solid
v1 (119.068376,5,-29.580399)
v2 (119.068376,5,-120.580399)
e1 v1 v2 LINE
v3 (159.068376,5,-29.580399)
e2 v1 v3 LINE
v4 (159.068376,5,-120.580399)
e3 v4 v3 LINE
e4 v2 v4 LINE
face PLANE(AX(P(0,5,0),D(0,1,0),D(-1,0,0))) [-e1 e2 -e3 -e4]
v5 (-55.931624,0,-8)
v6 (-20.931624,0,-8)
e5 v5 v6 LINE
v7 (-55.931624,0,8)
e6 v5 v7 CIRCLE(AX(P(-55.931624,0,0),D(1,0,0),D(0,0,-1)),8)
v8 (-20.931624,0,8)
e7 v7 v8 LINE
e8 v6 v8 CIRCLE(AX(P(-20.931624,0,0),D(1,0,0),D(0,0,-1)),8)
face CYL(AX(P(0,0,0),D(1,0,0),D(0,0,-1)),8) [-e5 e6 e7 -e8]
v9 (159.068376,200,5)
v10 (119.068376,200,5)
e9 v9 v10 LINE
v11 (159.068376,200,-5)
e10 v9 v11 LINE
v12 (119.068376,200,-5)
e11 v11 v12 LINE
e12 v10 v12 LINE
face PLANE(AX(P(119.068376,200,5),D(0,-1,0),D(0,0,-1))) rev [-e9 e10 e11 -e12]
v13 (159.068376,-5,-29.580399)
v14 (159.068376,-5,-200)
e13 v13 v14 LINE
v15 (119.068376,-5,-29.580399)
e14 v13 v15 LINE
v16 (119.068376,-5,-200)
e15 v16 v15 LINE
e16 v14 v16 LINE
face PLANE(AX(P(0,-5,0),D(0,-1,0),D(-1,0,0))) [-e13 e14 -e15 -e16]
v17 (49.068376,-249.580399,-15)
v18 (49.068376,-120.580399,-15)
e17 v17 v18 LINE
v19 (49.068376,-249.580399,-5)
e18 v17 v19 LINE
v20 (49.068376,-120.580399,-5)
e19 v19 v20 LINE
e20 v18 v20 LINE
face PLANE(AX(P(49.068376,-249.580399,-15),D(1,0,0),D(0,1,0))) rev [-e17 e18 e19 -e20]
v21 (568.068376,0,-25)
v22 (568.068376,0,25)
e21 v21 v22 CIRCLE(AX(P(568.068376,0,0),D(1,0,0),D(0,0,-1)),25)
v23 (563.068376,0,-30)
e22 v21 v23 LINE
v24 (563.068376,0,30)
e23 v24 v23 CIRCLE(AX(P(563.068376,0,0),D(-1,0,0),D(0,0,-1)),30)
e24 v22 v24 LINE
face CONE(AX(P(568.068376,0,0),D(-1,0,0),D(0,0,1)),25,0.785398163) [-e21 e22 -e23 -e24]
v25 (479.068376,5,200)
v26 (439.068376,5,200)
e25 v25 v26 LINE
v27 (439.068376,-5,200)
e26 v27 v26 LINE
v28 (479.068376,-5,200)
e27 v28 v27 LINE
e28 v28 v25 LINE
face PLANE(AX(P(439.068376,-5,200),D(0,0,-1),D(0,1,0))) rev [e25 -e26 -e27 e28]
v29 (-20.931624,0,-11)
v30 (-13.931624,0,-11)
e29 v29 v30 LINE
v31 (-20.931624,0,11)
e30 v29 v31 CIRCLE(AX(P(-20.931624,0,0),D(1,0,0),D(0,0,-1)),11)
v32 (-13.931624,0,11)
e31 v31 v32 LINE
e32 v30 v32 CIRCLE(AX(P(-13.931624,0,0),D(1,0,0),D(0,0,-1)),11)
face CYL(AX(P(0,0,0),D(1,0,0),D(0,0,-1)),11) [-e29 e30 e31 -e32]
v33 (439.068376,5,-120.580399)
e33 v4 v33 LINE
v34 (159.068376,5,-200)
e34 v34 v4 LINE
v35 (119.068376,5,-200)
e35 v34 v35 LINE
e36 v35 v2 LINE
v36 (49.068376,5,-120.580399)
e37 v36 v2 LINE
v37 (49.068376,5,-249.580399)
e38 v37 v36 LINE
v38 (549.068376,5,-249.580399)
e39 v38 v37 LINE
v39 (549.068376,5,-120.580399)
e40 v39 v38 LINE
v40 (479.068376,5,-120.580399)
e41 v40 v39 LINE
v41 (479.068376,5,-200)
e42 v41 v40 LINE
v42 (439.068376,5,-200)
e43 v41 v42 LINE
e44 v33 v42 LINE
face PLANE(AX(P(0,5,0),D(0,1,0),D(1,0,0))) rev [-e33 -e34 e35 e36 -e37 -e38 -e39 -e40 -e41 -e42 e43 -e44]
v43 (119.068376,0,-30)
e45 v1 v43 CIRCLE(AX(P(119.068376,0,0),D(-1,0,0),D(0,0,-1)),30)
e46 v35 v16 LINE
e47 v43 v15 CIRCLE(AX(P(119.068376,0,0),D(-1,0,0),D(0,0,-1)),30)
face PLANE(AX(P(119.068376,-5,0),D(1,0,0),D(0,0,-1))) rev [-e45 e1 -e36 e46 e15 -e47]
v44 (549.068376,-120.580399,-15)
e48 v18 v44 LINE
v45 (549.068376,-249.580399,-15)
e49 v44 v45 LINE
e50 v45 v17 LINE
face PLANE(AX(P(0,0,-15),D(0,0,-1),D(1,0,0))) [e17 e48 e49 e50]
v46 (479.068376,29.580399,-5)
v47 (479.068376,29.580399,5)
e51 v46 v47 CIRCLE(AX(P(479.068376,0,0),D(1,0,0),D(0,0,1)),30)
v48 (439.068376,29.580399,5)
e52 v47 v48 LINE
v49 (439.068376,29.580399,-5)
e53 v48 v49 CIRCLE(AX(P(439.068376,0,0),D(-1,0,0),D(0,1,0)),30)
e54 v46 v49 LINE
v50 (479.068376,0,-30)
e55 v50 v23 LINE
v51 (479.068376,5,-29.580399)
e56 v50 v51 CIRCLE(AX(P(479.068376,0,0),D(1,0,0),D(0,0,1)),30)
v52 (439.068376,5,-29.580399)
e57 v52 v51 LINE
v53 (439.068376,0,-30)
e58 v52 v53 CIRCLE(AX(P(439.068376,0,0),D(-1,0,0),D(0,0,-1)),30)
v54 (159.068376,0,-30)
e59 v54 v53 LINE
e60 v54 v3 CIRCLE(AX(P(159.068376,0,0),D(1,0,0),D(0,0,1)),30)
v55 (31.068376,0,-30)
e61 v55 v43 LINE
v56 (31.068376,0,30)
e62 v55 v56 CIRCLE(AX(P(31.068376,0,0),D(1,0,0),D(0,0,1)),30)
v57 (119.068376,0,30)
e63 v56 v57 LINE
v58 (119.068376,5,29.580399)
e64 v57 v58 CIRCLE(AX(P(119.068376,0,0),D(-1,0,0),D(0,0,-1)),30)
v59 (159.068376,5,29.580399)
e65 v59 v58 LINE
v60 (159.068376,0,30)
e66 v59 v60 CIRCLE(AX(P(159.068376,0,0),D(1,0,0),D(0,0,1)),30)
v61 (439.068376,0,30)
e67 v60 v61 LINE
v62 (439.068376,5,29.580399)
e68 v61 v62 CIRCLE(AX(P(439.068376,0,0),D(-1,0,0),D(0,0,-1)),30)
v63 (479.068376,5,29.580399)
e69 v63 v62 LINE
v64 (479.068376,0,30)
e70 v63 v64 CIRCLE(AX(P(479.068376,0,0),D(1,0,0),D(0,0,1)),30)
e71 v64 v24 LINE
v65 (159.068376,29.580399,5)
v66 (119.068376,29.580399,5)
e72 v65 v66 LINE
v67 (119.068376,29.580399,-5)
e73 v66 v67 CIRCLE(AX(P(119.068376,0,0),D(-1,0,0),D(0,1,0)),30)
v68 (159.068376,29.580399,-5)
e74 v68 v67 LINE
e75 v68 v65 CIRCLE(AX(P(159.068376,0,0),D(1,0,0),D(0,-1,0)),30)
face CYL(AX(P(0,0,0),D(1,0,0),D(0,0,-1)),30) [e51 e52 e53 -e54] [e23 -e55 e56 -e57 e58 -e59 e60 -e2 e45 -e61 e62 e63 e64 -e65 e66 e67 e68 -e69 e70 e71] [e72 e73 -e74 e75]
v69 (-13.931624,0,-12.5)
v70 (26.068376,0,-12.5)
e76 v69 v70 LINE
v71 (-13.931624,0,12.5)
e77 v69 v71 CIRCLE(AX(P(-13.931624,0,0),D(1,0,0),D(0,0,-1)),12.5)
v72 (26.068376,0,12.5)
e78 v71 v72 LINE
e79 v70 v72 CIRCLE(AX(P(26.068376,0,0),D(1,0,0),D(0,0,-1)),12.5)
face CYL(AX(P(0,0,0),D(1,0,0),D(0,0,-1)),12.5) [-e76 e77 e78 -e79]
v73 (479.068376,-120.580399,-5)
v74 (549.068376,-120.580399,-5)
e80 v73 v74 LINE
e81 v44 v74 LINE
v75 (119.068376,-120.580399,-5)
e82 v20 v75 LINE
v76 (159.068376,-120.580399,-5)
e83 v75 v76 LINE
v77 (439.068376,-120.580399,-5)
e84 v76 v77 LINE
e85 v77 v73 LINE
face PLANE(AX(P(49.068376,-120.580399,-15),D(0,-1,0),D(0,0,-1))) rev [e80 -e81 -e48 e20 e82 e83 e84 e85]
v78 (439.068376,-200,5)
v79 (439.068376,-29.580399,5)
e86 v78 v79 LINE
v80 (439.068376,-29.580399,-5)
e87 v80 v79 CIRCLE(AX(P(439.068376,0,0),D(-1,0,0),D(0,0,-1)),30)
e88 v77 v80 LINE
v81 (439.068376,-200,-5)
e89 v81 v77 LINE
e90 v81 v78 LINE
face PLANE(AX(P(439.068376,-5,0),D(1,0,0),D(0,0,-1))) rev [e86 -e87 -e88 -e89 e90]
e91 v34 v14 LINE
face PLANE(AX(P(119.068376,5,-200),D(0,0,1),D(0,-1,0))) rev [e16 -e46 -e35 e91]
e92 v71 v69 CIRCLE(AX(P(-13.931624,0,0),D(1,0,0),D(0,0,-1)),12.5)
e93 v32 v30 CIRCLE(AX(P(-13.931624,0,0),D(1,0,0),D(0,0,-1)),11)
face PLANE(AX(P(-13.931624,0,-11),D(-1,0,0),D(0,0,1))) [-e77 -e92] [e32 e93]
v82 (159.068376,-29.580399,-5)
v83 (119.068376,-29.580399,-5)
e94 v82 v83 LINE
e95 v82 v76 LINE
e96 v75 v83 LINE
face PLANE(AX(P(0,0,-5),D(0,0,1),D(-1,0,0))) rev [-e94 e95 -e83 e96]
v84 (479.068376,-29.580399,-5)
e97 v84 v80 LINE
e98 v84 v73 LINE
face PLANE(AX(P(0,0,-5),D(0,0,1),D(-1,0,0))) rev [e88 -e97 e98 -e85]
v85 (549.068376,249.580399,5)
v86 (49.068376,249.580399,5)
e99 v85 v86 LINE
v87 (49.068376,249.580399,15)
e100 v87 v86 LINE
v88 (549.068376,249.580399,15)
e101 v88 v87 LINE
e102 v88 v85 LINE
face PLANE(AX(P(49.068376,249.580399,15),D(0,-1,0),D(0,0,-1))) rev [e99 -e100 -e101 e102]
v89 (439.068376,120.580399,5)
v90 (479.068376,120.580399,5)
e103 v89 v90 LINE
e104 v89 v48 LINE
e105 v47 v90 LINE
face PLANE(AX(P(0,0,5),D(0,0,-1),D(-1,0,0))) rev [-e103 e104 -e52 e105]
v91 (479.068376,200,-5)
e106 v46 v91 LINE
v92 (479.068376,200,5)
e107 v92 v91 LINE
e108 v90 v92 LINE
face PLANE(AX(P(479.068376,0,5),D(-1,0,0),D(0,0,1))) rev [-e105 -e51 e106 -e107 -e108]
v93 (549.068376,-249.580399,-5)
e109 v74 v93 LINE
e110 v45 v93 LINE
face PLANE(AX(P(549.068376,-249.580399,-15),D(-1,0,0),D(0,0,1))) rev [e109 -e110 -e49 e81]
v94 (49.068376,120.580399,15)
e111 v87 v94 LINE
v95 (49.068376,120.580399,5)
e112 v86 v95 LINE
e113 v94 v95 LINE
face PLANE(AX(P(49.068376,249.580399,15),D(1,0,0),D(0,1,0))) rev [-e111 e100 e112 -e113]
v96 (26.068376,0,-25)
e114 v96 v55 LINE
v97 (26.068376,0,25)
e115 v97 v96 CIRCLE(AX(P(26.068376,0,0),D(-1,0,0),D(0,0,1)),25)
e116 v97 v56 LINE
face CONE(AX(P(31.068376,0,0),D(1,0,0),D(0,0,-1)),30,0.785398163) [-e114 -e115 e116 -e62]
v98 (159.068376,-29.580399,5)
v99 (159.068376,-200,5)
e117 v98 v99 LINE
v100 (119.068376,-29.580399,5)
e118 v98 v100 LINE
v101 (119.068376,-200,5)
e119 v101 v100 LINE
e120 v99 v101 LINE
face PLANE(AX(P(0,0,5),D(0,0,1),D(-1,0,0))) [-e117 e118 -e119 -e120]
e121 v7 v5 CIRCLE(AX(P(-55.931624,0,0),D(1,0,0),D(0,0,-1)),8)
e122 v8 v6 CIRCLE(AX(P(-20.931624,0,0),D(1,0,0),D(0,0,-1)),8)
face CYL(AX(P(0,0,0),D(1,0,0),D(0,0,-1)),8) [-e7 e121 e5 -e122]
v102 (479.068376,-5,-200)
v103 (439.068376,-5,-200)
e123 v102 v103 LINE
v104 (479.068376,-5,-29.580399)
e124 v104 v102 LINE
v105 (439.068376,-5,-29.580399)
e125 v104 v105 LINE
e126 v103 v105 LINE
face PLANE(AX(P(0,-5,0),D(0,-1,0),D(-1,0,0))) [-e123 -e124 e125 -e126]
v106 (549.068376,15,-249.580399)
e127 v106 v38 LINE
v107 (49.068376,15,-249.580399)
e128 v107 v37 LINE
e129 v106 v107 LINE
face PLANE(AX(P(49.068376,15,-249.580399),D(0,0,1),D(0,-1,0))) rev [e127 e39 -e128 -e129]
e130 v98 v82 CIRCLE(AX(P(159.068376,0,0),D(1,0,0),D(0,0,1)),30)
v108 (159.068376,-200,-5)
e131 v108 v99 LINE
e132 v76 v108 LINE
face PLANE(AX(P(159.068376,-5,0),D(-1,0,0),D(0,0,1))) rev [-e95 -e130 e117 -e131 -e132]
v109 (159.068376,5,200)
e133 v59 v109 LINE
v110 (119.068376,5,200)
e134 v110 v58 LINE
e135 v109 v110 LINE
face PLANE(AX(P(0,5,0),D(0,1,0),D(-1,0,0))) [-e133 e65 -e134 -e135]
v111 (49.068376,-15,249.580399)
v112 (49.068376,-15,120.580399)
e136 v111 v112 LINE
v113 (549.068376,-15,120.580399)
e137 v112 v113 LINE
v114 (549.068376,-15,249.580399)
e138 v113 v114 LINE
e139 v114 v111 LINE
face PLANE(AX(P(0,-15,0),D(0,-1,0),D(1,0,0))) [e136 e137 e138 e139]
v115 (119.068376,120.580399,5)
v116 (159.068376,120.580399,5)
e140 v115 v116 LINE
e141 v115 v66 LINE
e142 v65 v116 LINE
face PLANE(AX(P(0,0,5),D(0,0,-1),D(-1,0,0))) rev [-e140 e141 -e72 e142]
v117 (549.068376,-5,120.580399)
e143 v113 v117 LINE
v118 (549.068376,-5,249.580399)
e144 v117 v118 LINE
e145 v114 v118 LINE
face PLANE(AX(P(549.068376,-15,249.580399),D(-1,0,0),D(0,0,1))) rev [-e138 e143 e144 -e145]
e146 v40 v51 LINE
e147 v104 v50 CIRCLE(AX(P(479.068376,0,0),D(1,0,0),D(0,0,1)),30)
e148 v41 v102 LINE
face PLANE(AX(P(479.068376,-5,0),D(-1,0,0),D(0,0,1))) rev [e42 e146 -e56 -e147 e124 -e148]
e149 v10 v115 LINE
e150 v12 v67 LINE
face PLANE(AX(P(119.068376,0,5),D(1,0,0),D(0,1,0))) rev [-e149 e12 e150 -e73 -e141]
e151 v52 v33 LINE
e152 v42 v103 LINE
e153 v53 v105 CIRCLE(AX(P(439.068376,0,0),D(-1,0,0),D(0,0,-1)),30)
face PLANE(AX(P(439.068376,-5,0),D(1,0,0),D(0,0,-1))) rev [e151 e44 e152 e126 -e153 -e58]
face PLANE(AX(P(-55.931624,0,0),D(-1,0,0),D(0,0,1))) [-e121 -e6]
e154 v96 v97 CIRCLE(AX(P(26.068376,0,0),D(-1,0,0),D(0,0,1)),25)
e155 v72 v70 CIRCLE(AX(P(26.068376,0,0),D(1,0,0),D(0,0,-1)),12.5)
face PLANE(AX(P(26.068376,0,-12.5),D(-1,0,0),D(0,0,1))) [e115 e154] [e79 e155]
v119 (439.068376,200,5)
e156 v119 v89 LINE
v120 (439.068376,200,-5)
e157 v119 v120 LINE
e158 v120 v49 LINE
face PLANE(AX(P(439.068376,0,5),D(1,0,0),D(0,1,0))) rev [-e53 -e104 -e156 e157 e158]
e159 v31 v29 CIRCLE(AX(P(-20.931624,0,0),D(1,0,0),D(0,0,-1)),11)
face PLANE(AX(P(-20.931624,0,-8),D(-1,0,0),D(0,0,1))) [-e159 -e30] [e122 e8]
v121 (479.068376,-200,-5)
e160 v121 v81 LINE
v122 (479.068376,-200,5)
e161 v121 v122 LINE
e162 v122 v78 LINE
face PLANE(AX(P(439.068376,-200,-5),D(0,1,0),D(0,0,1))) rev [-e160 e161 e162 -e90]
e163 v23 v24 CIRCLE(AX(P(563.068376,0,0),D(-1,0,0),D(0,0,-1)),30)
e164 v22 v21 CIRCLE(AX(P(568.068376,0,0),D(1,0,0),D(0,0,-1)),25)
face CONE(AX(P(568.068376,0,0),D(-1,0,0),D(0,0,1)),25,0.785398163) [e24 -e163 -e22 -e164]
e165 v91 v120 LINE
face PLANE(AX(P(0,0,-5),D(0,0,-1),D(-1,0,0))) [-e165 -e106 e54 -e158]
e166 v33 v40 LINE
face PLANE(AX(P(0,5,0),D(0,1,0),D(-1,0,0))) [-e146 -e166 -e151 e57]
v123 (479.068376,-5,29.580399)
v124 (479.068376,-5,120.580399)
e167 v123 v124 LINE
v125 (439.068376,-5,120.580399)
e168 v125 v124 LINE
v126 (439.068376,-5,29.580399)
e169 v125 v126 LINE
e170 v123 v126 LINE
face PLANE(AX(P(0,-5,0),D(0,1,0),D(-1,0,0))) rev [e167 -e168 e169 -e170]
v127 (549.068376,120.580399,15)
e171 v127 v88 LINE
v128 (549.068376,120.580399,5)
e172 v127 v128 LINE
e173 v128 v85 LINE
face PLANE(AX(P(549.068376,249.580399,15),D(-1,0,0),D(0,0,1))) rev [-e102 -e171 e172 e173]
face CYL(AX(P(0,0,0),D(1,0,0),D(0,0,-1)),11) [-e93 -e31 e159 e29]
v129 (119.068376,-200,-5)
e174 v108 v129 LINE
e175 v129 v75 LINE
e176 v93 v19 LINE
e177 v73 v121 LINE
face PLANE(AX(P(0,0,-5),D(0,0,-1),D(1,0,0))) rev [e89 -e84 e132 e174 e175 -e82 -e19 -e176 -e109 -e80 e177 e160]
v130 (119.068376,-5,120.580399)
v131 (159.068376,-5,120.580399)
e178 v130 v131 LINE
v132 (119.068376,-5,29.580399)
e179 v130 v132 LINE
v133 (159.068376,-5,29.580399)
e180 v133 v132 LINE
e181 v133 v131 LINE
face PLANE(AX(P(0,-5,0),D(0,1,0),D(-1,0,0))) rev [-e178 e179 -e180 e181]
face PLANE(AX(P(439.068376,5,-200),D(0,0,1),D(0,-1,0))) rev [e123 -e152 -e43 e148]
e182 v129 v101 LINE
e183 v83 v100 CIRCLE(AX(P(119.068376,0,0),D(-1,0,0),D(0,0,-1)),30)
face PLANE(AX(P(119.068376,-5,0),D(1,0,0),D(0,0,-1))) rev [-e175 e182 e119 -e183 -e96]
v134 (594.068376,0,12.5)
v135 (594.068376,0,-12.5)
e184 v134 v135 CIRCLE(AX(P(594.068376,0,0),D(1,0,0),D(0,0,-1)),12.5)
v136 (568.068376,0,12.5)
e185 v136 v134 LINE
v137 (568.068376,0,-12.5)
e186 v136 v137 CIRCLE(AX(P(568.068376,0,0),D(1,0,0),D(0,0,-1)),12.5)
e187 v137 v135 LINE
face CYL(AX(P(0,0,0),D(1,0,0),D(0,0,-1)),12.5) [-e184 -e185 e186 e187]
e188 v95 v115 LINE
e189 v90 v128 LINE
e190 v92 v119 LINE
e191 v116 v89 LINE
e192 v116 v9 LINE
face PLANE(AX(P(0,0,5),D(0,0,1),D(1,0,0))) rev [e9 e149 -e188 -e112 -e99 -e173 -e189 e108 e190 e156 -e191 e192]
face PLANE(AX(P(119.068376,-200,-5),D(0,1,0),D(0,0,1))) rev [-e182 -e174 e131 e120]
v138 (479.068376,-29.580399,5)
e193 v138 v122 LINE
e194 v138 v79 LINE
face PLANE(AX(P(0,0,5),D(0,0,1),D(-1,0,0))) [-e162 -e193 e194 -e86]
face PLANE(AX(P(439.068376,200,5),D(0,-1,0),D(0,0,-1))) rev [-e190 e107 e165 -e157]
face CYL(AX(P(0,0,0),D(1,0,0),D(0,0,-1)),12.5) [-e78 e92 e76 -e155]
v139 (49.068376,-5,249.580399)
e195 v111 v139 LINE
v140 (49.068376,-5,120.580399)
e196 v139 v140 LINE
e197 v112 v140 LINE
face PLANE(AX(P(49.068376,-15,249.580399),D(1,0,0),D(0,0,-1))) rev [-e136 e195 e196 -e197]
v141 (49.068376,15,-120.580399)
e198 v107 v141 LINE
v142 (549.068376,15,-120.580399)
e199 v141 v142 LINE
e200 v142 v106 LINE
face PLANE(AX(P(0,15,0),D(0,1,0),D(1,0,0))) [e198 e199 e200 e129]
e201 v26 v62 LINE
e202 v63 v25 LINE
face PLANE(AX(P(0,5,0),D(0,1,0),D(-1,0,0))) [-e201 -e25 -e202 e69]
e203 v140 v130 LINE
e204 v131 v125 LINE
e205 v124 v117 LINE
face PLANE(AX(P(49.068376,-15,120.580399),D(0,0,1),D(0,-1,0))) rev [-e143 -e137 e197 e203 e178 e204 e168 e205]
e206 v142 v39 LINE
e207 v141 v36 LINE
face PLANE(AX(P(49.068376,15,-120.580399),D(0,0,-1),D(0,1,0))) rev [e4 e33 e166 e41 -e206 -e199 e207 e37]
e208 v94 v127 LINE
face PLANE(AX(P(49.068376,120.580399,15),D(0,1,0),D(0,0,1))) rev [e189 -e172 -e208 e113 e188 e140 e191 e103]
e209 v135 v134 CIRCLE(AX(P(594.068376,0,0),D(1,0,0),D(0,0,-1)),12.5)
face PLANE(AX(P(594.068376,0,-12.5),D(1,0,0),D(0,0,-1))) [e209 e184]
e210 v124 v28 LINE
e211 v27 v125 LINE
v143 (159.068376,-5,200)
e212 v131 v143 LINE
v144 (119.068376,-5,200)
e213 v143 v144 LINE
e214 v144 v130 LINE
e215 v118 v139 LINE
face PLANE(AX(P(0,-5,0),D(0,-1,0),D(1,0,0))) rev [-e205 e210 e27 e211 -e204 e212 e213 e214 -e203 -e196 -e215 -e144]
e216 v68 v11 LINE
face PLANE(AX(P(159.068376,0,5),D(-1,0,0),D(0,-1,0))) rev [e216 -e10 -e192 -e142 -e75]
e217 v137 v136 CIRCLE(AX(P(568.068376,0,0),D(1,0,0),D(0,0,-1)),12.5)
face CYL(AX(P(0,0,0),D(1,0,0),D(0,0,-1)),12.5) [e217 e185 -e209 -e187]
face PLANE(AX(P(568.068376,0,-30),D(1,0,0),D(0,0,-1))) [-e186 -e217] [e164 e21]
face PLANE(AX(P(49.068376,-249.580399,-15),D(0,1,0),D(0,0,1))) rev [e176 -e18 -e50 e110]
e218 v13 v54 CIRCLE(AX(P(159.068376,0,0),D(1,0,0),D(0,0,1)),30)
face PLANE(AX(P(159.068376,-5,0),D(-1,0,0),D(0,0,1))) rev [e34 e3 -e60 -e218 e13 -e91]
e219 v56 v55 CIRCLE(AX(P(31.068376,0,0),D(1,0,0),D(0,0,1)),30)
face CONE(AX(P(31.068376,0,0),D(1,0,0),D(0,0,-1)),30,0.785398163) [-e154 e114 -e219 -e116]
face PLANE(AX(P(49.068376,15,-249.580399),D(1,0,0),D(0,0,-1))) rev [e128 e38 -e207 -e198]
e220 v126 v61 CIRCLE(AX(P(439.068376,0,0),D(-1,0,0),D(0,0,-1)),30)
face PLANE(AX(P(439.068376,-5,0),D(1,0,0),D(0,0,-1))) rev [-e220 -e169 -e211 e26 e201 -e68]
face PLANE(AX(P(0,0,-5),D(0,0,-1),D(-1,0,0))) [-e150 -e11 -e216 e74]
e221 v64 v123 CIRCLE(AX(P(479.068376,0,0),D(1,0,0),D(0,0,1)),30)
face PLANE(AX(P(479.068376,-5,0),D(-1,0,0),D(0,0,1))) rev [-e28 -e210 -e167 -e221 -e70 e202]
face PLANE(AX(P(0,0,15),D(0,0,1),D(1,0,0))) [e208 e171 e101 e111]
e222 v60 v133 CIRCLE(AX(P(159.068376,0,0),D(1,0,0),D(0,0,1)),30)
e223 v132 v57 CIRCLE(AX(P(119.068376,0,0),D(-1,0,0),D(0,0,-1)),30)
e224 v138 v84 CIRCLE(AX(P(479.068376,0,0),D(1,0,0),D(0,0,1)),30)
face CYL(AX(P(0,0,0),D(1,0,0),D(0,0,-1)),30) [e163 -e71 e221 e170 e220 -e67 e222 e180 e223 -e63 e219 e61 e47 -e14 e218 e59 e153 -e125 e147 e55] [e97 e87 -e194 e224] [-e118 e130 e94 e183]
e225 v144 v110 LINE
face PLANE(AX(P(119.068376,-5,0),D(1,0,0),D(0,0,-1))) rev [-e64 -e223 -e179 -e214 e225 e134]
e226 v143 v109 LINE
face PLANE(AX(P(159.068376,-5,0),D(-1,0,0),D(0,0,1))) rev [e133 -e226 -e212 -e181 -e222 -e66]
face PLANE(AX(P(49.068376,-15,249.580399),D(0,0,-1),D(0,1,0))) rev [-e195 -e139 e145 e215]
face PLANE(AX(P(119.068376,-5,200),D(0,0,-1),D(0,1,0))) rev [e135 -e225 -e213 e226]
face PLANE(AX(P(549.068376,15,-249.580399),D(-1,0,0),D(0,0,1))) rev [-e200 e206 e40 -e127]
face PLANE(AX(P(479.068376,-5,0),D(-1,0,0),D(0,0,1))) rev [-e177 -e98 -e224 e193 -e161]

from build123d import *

# Parameters (mm, degrees)
CHAMFER1_SIZE       = 5
SKETCH3_W           = 40
SKETCH3_H           = 200
BOSS_EXTRUDE1_DEPTH = 5
SKETCH4_W           = 500
SKETCH4_H           = 129
BOSS_EXTRUDE2_DEPTH = 10
CIRPATTERN2_COUNT   = 4


with BuildPart() as part:
    # Sketch2 → Revolve1 (revolve)
    with BuildSketch(Plane(origin=(0, 0, 0), x_dir=(1, 0, 0), z_dir=(0, 1, 0))):
        Polygon((-55.931623932, 0), (-55.931623932, 8), (-20.931623932, 8), (-20.931623932, 11), (-13.931623932, 11), (-13.931623932, 12.5), (26.068376068, 12.5), (26.068376068, 30), (568.068376068, 30), (568.068376068, 12.5), (594.068376068, 12.5), (594.068376068, 0), align=None)
    revolve(axis=Axis((0, 0, 0), (-1, 0, 0)))

    # Chamfer1
    chamfer1_edges = [part.edges().sort_by_distance(p)[0] for p in [
        (26.068376068, 0, 30),
        (568.068376068, 0, 30),
    ]]
    chamfer(chamfer1_edges, length=CHAMFER1_SIZE)

    # Sketch3 → Boss-Extrude1 (add, symmetric)
    with BuildSketch(Plane.XY):
        with Locations((139.068376068, 100)):
            Rectangle(SKETCH3_W, SKETCH3_H)
        with Locations((459.068376068, 100)):
            Rectangle(SKETCH3_W, SKETCH3_H)
    boss_extrude1 = extrude(amount=BOSS_EXTRUDE1_DEPTH, both=True)

    # Sketch4 → Boss-Extrude2 (add)
    with BuildSketch(Plane.XY.offset(5)):
        with Locations((299.068376068, 185.080398915)):
            Rectangle(SKETCH4_W, SKETCH4_H)
    boss_extrude2 = extrude(amount=BOSS_EXTRUDE2_DEPTH)

    # CirPattern2: Boss-Extrude1, Boss-Extrude2 ×4 about axis
    cirpattern2_axis = Axis((0, 0, 0), (1, 0, 0))
    add([boss_extrude1.rotate(cirpattern2_axis, i * 360 / CIRPATTERN2_COUNT) for i in range(1, CIRPATTERN2_COUNT)])
    add([boss_extrude2.rotate(cirpattern2_axis, i * 360 / CIRPATTERN2_COUNT) for i in range(1, CIRPATTERN2_COUNT)])


solid = part.part
